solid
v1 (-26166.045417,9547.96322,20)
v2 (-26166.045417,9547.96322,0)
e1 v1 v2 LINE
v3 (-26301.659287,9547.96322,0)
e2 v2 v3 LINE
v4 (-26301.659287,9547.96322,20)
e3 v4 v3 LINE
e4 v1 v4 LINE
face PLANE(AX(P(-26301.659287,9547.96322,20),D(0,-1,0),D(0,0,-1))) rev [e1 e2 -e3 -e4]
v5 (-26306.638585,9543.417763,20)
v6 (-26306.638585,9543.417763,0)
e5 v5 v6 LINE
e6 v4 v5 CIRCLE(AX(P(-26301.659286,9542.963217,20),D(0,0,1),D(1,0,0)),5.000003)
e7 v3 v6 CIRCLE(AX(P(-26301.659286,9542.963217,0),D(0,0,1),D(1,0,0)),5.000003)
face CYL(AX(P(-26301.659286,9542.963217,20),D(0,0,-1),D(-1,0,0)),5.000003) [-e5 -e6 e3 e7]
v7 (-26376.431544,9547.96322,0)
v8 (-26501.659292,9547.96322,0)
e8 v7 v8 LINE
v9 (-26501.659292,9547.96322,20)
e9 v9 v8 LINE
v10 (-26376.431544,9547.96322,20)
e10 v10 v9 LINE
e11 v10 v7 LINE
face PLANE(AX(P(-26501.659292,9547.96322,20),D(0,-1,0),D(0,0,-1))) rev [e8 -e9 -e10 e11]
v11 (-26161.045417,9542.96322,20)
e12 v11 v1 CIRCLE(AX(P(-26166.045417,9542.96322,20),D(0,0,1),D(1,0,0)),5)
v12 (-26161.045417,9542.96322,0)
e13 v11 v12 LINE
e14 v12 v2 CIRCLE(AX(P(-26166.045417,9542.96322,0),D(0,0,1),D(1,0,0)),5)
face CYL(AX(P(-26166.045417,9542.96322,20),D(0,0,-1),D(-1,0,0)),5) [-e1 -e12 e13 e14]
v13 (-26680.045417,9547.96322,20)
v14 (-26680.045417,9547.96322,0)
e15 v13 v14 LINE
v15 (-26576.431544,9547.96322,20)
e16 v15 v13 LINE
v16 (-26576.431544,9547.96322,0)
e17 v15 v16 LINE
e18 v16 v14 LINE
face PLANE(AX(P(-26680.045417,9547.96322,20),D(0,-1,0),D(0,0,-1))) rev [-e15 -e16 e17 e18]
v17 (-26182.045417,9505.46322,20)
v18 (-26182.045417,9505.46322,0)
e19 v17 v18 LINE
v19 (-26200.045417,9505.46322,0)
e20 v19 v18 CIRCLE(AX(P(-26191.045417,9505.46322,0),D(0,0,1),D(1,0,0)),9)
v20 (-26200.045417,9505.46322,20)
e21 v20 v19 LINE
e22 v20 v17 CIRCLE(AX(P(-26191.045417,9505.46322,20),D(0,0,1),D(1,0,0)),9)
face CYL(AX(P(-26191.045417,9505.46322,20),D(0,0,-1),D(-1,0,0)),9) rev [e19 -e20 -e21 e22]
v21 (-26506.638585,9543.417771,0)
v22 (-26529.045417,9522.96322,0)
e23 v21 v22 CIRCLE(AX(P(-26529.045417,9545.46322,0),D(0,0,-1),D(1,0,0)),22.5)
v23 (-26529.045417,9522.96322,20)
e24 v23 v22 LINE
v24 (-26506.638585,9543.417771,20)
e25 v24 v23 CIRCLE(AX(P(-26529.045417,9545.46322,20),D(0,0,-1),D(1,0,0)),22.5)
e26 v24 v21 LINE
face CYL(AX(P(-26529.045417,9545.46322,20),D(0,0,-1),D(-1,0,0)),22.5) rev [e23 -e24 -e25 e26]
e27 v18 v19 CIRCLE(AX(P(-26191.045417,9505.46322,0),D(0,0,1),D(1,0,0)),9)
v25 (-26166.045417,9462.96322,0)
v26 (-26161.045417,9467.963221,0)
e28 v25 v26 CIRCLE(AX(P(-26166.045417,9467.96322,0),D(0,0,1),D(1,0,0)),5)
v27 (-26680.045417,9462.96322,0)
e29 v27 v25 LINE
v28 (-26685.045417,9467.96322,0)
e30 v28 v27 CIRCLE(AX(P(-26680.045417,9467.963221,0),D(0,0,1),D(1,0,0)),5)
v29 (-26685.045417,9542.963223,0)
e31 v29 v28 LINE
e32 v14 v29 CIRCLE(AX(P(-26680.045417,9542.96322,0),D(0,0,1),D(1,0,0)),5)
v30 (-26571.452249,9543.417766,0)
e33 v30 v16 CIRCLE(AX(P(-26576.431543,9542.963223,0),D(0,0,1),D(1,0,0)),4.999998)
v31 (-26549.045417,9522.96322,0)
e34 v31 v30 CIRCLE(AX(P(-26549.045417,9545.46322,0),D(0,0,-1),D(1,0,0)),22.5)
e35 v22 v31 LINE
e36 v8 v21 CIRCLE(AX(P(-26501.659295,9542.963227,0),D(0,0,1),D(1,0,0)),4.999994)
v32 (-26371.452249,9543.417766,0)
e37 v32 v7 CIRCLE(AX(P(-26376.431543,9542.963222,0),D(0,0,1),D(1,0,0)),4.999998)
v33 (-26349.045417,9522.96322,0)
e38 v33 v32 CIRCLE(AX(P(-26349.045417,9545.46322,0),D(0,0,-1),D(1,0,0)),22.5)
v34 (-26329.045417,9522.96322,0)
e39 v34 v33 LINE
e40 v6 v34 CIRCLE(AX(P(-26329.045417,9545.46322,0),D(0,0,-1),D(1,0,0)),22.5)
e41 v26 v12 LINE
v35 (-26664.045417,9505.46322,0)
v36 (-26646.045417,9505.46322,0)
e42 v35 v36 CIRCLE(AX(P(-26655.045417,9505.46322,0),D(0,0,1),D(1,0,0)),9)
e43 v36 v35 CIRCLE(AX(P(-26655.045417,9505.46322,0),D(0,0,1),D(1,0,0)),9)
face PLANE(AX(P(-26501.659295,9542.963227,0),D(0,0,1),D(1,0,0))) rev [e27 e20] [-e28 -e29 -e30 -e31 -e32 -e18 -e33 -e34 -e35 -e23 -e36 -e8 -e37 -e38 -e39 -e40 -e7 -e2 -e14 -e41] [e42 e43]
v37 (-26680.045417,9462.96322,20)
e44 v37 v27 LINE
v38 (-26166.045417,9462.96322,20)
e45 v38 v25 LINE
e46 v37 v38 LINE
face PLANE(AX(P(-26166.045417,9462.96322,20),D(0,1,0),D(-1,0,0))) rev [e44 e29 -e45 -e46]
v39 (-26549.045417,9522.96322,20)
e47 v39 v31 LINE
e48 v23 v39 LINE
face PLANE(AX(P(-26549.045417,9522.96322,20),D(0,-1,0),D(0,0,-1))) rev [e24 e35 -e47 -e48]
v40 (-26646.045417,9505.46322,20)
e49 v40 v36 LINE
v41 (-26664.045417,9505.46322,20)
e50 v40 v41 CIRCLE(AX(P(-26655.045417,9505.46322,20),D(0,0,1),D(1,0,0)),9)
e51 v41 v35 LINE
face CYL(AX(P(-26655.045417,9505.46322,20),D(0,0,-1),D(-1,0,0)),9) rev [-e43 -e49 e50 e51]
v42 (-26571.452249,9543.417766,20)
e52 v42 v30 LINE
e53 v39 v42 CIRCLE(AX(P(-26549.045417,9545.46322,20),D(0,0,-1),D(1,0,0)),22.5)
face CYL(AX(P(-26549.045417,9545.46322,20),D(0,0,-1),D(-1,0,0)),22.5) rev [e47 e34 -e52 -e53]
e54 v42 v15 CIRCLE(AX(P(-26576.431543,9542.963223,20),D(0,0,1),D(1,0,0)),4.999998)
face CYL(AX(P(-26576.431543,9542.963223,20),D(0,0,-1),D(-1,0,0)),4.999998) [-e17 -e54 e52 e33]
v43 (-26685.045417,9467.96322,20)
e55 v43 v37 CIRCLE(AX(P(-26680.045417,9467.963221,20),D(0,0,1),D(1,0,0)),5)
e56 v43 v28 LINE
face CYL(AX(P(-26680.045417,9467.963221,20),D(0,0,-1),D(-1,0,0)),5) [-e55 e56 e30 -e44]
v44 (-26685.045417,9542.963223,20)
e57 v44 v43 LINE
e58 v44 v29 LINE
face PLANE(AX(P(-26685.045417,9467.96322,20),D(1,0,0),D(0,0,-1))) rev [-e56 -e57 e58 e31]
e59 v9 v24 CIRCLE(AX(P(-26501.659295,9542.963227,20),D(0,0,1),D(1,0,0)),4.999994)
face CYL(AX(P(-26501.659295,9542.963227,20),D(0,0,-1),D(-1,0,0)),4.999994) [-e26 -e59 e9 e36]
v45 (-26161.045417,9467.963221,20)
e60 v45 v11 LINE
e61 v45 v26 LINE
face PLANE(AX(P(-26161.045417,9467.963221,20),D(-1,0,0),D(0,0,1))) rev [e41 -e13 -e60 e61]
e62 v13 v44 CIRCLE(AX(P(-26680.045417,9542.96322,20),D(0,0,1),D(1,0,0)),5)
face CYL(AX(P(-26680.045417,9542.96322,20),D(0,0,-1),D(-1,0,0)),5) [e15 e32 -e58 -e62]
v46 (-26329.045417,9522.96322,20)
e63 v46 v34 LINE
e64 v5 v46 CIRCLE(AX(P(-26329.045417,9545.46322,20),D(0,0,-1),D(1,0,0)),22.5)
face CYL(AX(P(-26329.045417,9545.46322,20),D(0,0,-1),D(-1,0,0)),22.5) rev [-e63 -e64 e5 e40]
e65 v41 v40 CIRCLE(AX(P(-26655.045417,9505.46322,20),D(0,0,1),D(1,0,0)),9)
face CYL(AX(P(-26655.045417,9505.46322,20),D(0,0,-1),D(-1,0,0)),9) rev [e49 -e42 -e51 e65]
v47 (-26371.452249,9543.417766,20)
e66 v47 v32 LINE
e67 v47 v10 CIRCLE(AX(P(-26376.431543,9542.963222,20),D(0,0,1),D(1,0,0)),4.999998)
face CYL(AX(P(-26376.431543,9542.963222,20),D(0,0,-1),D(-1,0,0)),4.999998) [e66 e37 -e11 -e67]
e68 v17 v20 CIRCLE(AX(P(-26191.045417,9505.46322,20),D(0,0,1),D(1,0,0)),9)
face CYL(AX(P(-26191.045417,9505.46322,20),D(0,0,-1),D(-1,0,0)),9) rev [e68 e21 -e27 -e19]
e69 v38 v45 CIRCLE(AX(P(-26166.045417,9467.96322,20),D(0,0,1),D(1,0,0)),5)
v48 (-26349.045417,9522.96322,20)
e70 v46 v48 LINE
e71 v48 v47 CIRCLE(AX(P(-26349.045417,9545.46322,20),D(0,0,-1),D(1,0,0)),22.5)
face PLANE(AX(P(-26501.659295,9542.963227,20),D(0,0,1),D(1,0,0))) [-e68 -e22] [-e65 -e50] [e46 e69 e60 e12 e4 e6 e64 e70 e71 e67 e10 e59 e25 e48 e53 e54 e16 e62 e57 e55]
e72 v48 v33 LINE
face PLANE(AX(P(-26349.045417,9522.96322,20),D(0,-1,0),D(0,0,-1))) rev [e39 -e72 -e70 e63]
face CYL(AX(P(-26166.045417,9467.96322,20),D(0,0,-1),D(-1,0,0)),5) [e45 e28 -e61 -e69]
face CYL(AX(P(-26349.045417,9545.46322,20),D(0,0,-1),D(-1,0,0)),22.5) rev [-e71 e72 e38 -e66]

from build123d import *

# Parameters (mm, degrees)
SKETCH1_R           = 9
BOSS_EXTRUDE1_DEPTH = 20


with BuildPart() as part:
    # Sketch1 → Boss-Extrude1 (new body)
    with BuildSketch(Plane.XY):
        with BuildLine():
            Line((-26685.045416981, 9467.963220498), (-26685.045416981, 9542.963223042))
            ThreePointArc((-26685.045416981, 9542.963223042), (-26683.580949969, 9546.498755277), (-26680.045416963, 9547.96322043))
            Line((-26680.045416963, 9547.96322043), (-26576.431543676, 9547.96322043))
            ThreePointArc((-26576.431543676, 9547.96322043), (-26573.060544526, 9546.655965332), (-26571.452248862, 9543.417765798))
            ThreePointArc((-26571.452248862, 9543.417765798), (-26564.214913831, 9528.845869116), (-26549.045416948, 9522.963220428))
            Line((-26549.045416948, 9522.963220428), (-26529.045416963, 9522.963220428))
            ThreePointArc((-26529.045416963, 9522.963220428), (-26513.875918272, 9528.845870766), (-26506.638584632, 9543.417770687))
            ThreePointArc((-26506.638584632, 9543.417770687), (-26505.030289423, 9546.655967321), (-26501.659292496, 9547.963220408))
            Line((-26501.659292496, 9547.963220408), (-26376.431544058, 9547.963220408))
            ThreePointArc((-26376.431544058, 9547.963220408), (-26373.060544852, 9546.655965256), (-26371.452248862, 9543.417765804))
            ThreePointArc((-26371.452248862, 9543.417765804), (-26364.214913847, 9528.845869098), (-26349.045416954, 9522.963220397))
            Line((-26349.045416954, 9522.963220397), (-26329.045416961, 9522.963220397))
            ThreePointArc((-26329.045416961, 9522.963220397), (-26313.875920919, 9528.845868323), (-26306.638585232, 9543.417763496))
            ThreePointArc((-26306.638585232, 9543.417763496), (-26305.03028784, 9546.655964088), (-26301.659287339, 9547.963220451))
            Line((-26301.659287339, 9547.963220451), (-26289.045416951, 9547.963220451))
            Line((-26289.045416951, 9547.963220451), (-26166.045416928, 9547.963220451))
            ThreePointArc((-26166.045416928, 9547.963220451), (-26162.509883026, 9546.498754363), (-26161.045416939, 9542.96322046))
            Line((-26161.045416939, 9542.96322046), (-26161.045416939, 9467.96322112))
            ThreePointArc((-26161.045416939, 9467.96322112), (-26162.509882821, 9464.42768677), (-26166.045416981, 9462.96322043))
            Line((-26166.045416981, 9462.96322043), (-26680.045417049, 9462.96322043))
            ThreePointArc((-26680.045417049, 9462.96322043), (-26683.580950913, 9464.427686595), (-26685.045416981, 9467.963220498))
        make_face()
        with Locations((-26655.045416981, 9505.46322043)):
            Circle(SKETCH1_R, mode=Mode.SUBTRACT)
        with Locations((-26191.045416981, 9505.46322043)):
            Circle(SKETCH1_R, mode=Mode.SUBTRACT)
    extrude(amount=BOSS_EXTRUDE1_DEPTH)


solid = part.part
